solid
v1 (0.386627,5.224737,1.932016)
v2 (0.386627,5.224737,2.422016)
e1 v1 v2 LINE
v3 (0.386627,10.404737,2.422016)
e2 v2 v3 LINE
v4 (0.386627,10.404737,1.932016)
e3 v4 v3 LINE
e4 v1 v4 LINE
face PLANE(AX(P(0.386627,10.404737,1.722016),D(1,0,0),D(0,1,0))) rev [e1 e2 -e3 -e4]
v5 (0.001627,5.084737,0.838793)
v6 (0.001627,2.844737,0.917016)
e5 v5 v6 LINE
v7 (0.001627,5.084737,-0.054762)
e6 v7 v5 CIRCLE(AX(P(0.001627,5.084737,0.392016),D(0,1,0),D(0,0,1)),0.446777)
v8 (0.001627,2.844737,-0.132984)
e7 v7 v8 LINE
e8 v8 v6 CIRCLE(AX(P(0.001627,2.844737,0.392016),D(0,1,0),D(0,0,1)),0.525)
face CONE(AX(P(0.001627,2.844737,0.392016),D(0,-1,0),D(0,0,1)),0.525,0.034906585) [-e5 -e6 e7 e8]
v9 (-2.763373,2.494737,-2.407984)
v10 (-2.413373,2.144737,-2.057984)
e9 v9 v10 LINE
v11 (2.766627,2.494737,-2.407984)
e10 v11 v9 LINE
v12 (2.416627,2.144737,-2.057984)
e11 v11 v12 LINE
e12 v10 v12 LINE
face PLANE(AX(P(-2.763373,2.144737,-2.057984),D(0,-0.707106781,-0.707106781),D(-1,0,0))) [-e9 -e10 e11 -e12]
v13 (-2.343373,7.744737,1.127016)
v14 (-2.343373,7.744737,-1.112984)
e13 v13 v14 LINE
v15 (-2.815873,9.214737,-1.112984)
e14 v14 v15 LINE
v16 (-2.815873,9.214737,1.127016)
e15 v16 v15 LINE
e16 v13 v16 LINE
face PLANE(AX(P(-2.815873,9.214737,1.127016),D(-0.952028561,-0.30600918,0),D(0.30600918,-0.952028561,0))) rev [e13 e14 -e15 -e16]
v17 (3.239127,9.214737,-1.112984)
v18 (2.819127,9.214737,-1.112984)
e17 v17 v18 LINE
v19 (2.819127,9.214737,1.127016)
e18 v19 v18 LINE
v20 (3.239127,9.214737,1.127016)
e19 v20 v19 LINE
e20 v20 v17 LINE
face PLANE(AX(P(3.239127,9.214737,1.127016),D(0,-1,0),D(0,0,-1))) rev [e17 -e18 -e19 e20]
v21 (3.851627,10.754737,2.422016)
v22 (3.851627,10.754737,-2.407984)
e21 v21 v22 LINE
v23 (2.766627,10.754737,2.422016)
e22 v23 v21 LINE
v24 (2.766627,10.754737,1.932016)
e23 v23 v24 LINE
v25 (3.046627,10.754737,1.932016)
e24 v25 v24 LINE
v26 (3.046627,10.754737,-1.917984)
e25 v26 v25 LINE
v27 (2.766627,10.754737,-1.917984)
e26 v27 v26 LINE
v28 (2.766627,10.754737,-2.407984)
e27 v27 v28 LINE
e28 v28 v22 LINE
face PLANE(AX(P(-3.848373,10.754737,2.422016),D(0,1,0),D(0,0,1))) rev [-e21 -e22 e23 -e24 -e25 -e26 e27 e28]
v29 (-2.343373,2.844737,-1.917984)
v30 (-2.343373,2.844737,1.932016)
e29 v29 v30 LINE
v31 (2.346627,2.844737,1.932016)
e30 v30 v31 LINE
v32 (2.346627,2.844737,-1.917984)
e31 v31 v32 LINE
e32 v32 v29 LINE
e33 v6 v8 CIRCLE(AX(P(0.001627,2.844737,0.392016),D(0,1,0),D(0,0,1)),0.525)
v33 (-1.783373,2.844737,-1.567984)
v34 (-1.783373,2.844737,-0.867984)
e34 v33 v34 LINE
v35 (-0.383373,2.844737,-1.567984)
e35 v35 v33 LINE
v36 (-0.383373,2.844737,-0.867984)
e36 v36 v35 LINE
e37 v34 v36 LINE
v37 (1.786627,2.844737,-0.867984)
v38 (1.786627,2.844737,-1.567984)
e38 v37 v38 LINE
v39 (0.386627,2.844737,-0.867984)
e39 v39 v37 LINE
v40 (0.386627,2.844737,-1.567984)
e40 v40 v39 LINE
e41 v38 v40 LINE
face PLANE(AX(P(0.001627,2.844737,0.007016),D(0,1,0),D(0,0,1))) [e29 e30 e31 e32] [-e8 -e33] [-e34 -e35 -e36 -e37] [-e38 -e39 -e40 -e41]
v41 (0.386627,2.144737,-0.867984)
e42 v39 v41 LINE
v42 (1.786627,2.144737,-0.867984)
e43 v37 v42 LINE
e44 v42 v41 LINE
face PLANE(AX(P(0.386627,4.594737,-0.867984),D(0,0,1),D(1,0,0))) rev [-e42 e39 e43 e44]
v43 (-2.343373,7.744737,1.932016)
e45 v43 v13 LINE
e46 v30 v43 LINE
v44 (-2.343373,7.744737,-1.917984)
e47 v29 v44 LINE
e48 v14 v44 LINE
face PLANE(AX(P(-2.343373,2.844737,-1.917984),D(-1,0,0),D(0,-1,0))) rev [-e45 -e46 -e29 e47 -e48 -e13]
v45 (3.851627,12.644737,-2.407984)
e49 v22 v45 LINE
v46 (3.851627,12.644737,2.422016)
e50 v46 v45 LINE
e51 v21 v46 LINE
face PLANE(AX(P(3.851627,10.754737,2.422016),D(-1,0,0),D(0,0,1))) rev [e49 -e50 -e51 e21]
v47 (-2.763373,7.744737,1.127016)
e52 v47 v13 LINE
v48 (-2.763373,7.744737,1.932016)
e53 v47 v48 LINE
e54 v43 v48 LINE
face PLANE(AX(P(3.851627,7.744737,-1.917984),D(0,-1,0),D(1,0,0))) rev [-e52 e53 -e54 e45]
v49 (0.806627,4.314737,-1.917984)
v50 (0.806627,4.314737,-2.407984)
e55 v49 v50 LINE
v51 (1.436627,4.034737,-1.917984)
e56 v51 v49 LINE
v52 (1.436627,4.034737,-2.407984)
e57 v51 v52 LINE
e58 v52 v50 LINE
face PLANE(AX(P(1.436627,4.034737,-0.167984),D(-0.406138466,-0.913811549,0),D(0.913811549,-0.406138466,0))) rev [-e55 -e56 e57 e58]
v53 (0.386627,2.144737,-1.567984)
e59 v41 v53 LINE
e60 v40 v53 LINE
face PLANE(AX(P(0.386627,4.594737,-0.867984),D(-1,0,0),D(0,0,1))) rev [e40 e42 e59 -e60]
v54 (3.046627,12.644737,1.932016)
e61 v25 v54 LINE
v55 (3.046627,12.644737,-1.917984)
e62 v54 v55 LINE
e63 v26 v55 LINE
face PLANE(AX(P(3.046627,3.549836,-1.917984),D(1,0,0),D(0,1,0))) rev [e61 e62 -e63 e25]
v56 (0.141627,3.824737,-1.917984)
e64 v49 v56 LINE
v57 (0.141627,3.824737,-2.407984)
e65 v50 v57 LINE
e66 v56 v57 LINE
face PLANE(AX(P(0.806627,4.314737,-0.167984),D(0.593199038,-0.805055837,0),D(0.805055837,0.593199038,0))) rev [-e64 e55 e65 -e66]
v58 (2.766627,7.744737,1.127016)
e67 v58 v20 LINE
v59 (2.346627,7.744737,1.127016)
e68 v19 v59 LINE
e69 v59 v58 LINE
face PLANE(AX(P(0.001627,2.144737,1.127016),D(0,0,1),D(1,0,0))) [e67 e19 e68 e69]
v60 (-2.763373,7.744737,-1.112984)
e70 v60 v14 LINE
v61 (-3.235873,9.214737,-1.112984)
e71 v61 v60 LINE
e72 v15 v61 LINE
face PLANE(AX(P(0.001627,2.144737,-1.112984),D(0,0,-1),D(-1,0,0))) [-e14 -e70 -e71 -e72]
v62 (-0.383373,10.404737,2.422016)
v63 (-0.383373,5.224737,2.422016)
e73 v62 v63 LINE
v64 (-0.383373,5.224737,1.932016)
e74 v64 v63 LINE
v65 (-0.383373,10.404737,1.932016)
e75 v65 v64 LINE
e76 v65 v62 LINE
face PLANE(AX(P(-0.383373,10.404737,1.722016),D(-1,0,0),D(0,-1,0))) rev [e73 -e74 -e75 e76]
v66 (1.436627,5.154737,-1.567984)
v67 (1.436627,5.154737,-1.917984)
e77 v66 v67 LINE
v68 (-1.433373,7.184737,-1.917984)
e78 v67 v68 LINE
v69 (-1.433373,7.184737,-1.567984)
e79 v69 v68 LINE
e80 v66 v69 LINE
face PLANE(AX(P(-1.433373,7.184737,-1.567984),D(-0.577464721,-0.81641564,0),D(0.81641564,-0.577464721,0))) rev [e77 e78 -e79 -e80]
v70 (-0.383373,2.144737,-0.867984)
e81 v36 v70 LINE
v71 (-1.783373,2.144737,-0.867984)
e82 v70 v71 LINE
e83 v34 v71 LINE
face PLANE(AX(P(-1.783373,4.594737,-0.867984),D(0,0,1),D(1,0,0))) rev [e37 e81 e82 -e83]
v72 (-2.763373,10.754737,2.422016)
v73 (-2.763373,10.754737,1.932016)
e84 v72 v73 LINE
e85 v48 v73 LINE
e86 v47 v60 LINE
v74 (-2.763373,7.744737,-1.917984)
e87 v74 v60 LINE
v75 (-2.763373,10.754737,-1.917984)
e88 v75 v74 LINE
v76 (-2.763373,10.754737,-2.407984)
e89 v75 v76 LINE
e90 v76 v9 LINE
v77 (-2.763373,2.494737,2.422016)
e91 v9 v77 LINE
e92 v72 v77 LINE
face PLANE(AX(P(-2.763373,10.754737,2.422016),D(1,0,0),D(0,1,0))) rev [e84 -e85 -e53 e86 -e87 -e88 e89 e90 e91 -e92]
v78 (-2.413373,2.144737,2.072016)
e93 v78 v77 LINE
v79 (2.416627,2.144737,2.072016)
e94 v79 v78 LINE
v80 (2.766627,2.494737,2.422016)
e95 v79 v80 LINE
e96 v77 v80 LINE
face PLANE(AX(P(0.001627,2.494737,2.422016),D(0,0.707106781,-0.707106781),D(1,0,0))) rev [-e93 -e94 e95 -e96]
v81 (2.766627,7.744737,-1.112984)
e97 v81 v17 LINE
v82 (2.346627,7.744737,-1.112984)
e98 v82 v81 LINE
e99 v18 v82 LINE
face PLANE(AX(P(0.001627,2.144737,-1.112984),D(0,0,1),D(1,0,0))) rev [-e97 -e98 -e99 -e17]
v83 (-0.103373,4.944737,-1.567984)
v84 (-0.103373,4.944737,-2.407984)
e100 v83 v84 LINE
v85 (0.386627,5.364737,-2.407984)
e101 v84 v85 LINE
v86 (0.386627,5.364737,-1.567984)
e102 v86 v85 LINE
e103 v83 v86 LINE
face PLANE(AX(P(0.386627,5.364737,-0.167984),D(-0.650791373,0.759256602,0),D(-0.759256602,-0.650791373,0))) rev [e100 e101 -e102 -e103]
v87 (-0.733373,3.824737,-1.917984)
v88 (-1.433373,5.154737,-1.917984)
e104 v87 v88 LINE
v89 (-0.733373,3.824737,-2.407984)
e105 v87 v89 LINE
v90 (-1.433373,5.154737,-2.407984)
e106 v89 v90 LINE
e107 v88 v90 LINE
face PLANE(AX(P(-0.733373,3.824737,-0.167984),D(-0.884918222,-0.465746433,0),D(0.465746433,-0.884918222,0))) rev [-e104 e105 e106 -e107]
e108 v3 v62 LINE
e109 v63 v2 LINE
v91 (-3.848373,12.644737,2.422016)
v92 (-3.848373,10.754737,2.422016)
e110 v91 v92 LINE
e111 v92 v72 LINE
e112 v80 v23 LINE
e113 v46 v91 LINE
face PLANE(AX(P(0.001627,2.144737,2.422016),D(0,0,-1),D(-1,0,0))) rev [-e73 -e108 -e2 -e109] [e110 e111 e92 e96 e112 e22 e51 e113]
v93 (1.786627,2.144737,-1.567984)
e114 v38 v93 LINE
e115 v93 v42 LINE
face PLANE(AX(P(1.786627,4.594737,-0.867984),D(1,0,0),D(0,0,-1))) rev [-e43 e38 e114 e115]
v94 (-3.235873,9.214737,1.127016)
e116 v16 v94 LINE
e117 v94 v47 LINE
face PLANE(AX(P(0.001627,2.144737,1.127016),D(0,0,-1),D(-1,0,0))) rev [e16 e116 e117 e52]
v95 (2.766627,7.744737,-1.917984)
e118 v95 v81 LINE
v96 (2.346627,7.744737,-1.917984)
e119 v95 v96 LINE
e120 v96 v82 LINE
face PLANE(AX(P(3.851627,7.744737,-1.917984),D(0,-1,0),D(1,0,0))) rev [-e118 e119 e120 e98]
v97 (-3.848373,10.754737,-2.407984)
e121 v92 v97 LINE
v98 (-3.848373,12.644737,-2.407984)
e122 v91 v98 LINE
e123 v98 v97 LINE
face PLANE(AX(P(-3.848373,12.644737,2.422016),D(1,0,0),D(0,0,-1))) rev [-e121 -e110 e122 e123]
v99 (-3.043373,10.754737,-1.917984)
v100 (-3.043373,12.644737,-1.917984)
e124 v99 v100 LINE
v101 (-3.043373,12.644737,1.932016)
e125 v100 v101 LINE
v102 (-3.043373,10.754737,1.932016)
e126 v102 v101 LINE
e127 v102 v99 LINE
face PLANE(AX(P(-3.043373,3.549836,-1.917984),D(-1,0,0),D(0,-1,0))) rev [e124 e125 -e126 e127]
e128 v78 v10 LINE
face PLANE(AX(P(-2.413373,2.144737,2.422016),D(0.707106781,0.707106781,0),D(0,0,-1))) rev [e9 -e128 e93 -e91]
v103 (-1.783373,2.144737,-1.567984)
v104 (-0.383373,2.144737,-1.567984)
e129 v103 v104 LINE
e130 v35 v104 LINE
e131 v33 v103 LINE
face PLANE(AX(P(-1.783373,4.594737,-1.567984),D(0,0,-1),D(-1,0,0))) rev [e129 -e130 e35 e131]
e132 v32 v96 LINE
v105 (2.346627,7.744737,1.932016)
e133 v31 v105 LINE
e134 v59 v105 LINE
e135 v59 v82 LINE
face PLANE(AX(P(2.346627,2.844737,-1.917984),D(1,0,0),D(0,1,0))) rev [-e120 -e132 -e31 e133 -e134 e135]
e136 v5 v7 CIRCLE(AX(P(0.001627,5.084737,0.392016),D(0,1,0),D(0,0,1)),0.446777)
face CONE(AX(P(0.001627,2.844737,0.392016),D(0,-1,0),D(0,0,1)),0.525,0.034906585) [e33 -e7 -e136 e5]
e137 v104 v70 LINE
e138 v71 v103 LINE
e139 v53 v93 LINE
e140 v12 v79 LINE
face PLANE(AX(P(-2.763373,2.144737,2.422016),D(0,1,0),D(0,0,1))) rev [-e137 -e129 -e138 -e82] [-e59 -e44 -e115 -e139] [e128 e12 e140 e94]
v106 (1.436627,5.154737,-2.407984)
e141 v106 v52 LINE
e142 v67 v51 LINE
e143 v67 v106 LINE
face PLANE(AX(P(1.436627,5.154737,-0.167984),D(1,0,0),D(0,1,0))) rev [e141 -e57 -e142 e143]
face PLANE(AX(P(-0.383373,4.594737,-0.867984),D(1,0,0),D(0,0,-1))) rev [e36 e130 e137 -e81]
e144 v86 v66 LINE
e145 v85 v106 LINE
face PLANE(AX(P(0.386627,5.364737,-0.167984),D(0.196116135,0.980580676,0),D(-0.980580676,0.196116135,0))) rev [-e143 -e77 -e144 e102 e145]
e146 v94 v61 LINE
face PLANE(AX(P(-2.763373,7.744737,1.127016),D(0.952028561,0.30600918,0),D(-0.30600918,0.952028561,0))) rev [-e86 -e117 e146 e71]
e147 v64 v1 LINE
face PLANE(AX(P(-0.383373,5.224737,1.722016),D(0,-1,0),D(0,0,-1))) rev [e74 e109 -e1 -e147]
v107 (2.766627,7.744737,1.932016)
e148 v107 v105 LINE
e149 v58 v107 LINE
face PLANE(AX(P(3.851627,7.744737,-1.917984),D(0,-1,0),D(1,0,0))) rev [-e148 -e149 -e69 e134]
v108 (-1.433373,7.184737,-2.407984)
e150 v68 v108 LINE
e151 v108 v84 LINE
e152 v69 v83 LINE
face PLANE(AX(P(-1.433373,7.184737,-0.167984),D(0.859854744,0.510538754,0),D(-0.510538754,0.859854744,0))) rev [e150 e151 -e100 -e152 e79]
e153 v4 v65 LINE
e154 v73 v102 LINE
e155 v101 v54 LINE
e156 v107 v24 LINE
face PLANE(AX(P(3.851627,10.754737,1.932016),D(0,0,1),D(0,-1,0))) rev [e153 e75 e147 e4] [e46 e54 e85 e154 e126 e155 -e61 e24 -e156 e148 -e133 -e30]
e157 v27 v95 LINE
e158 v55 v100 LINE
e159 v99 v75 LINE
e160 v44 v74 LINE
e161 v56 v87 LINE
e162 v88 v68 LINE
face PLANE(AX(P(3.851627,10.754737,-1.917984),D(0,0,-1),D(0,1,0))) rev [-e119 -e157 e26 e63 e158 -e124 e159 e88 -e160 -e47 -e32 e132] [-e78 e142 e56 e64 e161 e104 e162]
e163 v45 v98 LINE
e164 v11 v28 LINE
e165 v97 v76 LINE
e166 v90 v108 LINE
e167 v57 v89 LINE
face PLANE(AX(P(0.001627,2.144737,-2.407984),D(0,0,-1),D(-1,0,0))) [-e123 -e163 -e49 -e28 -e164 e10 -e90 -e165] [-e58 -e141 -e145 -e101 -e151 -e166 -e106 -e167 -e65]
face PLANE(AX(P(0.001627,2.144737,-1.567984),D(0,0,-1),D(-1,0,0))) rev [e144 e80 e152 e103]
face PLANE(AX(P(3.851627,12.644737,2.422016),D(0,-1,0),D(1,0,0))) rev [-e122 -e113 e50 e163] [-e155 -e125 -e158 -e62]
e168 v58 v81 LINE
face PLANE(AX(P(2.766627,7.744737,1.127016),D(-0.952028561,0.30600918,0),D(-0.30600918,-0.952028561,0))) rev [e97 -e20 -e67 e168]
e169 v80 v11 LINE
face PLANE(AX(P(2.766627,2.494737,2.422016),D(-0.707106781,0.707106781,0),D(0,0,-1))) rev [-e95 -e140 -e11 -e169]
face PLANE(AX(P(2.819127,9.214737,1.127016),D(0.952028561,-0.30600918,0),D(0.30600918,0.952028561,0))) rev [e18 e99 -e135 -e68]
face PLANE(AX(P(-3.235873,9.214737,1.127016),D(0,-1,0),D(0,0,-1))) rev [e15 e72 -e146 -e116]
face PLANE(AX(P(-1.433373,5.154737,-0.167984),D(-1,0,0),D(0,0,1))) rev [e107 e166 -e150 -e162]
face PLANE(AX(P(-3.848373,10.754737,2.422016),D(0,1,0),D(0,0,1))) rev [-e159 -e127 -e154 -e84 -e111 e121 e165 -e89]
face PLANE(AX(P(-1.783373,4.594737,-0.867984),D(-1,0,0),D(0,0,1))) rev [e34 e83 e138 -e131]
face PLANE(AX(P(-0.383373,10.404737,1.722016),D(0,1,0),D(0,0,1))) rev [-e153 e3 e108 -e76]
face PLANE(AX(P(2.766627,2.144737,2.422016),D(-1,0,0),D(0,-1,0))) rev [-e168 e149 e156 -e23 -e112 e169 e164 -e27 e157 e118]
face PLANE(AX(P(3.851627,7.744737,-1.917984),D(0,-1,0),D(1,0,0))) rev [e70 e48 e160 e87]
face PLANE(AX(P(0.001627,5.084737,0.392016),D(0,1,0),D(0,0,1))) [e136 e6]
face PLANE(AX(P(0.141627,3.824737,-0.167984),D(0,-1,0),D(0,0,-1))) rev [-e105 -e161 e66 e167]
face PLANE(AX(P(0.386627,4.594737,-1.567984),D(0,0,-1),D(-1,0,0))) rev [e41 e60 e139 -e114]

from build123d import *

# Parameters (mm, degrees)
EXTRUDE_1_DEPTH     = 3.45
CHAMFER_1_SIZE      = 0.5
SKETCH_2_W          = 5.5
SKETCH_2_H          = 4.3
CUT_EXTRUDE_1_DEPTH = 19.061146143
SKETCH_3_W          = 8.7
SKETCH_3_H          = 5.5
CUT_EXTRUDE_2_DEPTH = 2.7
SKETCH_5_W          = 6.7
SKETCH_5_H          = 5.5
CUT_EXTRUDE_3_DEPTH = 14
SKETCH_6_W          = 1.1
SKETCH_6_H          = 7.4
CUT_EXTRUDE_4_DEPTH = 1
EXTRUDE_2_DEPTH     = 1.6
SKETCH_8_W          = 2
SKETCH_8_H          = 1
CUT_EXTRUDE_5_DEPTH = 3.5
SKETCH_9_R          = 0.75
EXTRUDE_3_DEPTH     = 3.2
DRAFT_1_ANGLE       = 2
CUT_EXTRUDE_6_DEPTH = 3.2
EXTRUDE_4_DEPTH     = 0.5
SCALE_1_SCALE       = 0.7


with BuildPart() as part:
    # 草图1 → 凸台-拉伸1 (new, symmetric)
    with BuildSketch(Plane.XY):
        Polygon((-3.95, 0), (3.95, 0), (3.95, 12.3), (5.5, 12.3), (5.5, 15), (-5.5, 15), (-5.5, 12.3), (-3.95, 12.3), align=None)
    extrude(amount=EXTRUDE_1_DEPTH, both=True)

    # 倒角1
    chamfer_1_edges = [part.edges().sort_by_distance(p)[0] for p in [
        (3.95, 0, 0),
        (-3.95, 0, 0),
        (0, 0, 3.45),
        (0, 0, -3.45),
    ]]
    chamfer(chamfer_1_edges, length=CHAMFER_1_SIZE)

    # 草图2 → 切除-拉伸1 (cut, through all)
    with BuildSketch(Plane.ZY.offset(3.95)):
        with Locations((0, 10.15)):
            Rectangle(SKETCH_2_W, SKETCH_2_H)
    extrude(amount=-CUT_EXTRUDE_1_DEPTH, mode=Mode.SUBTRACT)

    # 草图3 → 切除-拉伸2 (cut)
    with BuildSketch(Plane(origin=(0, 15, 0), x_dir=(1, 0, 0), z_dir=(0, 1, 0))):
        Rectangle(SKETCH_3_W, SKETCH_3_H)
    extrude(amount=-CUT_EXTRUDE_2_DEPTH, mode=Mode.SUBTRACT)

    # 草图5 → 切除-拉伸3 (cut)
    with BuildSketch(Plane(origin=(0, 15, 0), x_dir=(1, 0, 0), z_dir=(0, 1, 0))):
        Rectangle(SKETCH_5_W, SKETCH_5_H)
    extrude(amount=-CUT_EXTRUDE_3_DEPTH, mode=Mode.SUBTRACT)

    # 草图6 → 切除-拉伸4 (cut)
    with BuildSketch(Plane.XY.offset(3.45)):
        with Locations((0, 8.1)):
            Rectangle(SKETCH_6_W, SKETCH_6_H)
    extrude(amount=-CUT_EXTRUDE_4_DEPTH, mode=Mode.SUBTRACT)

    # 草图7 → 凸台-拉伸2 (add, symmetric)
    with BuildSketch(Plane.XY):
        Polygon((-3.95, 8), (-4.625, 10.1), (-4.025, 10.1), (-3.35, 8), align=None)
        Polygon((3.35, 8), (3.95, 8), (4.625, 10.1), (4.025, 10.1), align=None)
    extrude(amount=EXTRUDE_2_DEPTH, both=True)

    # 草图8 → 切除-拉伸5 (cut)
    with BuildSketch(Plane.XZ):
        with Locations((-1.55, -1.75)):
            Rectangle(SKETCH_8_W, SKETCH_8_H)
        with Locations((1.55, -1.75)):
            Rectangle(SKETCH_8_W, SKETCH_8_H)
    extrude(amount=-CUT_EXTRUDE_5_DEPTH, mode=Mode.SUBTRACT)

    # 草图9 → 凸台-拉伸3 (add)
    with BuildSketch(Plane(origin=(0, 1, 0), x_dir=(1, 0, 0), z_dir=(0, 1, 0))):
        with Locations(Location((0, -0.55, 0), (0, 0, 270))):
            Circle(SKETCH_9_R)
    extrude(amount=EXTRUDE_3_DEPTH)

    # 拔模1
    draft_1_faces = [part.faces().sort_by_distance(p)[0] for p in [
        (0, 2.6, -0.2),
    ]]
    draft(draft_1_faces, Plane.ZX.offset(1), DRAFT_1_ANGLE)

    # 草图10 → 切除-拉伸6 (cut)
    with BuildSketch(Plane(origin=(0, 0, -3.45), x_dir=(-1, 0, 0), z_dir=(0, 0, -1))):
        Polygon((-2.05, 4.3), (-2.05, 2.7), (-1.15, 3.1), (-0.2, 2.4), (1.05, 2.4), (2.05, 4.3), (2.05, 7.2), (0.15, 4), (-0.55, 4.6), align=None)
    extrude(amount=-CUT_EXTRUDE_6_DEPTH, mode=Mode.SUBTRACT)

    # 草图11 → 凸台-拉伸4 (add)
    with BuildSketch(Plane.XY.offset(-2.75)):
        Polygon((0.55, 4.6), (2.05, 4.3), (-2.05, 7.2), (-0.15, 4), align=None)
    extrude(amount=EXTRUDE_4_DEPTH)


with BuildPart() as part_1:
    # 缩放比例1: scaled about (0.005424554, 7.149122165, 0.023385792)
    add(part.part.scale(SCALE_1_SCALE).moved(Location((0.001627366, 2.14473665, 0.007015738))))


solid = part_1.part
